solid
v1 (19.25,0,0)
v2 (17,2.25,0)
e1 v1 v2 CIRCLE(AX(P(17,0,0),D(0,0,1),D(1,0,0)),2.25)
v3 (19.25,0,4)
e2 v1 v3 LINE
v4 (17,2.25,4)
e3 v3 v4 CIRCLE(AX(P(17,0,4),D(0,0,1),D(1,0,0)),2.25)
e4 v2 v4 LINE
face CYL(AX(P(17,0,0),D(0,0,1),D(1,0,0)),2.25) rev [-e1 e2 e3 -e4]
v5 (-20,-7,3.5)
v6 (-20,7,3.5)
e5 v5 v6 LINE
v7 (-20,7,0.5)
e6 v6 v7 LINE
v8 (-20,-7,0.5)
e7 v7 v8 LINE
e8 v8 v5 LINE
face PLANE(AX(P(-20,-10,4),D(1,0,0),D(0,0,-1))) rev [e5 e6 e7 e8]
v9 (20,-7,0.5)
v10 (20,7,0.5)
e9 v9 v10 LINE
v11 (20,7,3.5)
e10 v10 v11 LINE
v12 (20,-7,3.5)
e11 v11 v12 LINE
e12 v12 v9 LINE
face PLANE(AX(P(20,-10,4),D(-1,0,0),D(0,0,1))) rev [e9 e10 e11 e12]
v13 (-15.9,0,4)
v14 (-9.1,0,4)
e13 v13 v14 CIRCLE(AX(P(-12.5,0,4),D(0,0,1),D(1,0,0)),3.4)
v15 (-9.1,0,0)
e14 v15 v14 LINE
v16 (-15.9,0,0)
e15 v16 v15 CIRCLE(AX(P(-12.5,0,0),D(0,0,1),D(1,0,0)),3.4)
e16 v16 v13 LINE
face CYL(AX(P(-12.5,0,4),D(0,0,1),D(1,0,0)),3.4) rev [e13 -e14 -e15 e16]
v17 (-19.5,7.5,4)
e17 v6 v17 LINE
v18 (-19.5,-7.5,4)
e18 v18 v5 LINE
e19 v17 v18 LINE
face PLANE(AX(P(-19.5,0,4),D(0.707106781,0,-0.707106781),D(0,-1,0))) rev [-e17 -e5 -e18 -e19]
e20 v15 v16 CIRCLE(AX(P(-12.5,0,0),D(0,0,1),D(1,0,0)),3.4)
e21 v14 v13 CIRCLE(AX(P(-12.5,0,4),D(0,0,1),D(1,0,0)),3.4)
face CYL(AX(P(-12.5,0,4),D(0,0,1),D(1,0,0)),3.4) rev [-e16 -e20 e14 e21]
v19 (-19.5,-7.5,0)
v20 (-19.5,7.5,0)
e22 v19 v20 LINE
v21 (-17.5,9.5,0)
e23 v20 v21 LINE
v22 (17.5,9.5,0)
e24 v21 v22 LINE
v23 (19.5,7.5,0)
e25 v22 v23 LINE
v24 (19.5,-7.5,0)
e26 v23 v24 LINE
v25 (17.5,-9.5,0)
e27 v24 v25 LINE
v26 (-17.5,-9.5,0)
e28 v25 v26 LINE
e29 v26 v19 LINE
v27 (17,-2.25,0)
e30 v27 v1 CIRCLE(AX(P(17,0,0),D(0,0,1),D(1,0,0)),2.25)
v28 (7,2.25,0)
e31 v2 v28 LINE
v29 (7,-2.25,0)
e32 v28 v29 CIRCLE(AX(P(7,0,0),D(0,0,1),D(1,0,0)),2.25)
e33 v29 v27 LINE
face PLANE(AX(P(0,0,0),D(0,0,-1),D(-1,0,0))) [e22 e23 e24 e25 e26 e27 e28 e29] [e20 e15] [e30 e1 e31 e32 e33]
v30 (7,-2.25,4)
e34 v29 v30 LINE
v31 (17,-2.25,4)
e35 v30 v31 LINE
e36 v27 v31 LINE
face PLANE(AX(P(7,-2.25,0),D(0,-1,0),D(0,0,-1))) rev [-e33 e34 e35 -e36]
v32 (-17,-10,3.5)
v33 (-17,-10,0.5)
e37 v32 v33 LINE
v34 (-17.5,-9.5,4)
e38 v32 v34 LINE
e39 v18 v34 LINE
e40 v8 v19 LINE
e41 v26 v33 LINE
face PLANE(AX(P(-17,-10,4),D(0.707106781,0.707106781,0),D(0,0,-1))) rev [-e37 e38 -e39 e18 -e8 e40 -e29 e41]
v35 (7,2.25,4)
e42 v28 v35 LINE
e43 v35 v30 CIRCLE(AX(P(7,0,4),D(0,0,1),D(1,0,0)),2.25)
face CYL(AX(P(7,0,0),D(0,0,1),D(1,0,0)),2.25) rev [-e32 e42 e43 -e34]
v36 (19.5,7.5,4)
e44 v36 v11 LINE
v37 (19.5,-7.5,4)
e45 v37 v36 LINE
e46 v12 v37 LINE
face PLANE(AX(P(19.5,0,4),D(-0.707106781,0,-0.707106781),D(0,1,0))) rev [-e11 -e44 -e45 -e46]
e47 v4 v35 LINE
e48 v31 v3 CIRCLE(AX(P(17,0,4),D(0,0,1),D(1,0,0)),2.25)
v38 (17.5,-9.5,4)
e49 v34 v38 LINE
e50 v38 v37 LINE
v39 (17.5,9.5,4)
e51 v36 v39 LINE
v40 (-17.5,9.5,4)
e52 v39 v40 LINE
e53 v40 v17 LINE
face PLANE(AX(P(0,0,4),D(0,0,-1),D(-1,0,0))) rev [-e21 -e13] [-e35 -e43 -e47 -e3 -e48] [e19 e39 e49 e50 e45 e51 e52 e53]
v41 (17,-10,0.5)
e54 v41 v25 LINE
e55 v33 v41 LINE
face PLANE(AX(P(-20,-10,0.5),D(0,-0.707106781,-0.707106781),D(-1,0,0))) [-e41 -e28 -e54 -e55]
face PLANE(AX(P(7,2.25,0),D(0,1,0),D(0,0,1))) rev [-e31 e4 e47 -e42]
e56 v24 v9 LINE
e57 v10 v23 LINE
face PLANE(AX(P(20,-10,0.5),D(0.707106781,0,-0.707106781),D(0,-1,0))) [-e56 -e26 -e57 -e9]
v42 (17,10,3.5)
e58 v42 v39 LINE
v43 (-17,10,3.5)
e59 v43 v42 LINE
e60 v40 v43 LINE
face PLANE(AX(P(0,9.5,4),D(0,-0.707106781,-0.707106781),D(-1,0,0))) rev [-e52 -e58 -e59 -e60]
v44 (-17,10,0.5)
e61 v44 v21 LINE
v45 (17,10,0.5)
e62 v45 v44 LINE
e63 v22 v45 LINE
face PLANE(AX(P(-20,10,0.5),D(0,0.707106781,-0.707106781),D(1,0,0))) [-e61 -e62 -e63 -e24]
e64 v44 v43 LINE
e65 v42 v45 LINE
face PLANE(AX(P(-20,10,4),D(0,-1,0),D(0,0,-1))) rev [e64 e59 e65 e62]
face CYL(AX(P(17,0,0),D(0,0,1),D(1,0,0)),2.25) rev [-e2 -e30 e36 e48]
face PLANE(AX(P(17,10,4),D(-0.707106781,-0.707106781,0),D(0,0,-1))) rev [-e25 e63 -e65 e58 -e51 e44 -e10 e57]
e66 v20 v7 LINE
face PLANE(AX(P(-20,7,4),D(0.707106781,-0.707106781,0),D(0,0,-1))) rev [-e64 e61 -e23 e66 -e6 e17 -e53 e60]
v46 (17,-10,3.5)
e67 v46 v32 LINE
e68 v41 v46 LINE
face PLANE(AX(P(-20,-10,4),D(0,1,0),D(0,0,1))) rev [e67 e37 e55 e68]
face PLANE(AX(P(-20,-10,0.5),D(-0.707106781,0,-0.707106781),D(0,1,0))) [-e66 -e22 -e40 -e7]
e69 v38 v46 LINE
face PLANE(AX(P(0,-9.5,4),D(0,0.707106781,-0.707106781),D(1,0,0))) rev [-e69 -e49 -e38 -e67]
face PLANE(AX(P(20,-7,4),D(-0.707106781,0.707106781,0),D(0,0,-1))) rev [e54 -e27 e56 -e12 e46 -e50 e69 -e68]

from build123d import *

# Parameters (mm, degrees)
SKETCH1_W           = 40
SKETCH1_H           = 20
BOSS_EXTRUDE1_DEPTH = 4
M8_TAPPED_HOLE1_D   = 6.8
CUT_EXTRUDE1_DEPTH  = 4
CHAMFER1_SIZE       = 3
CHAMFER2_SIZE       = 0.5


with BuildPart() as part:
    # Sketch1 → Boss-Extrude1 (new body)
    with BuildSketch(Plane.XY):
        Rectangle(SKETCH1_W, SKETCH1_H)
    extrude(amount=BOSS_EXTRUDE1_DEPTH)

    # M8 Tapped Hole1 (through all)
    with Locations(Plane.XY.offset(4)):
        with Locations((-12.5, 0)):
            Hole(M8_TAPPED_HOLE1_D / 2)

    # Sketch4 → Cut-Extrude1 (cut)
    with BuildSketch(Plane.XY.offset(4)):
        with BuildLine():
            Line((7, 2.25), (17, 2.25))
            ThreePointArc((17, 2.25), (19.25, 0), (17, -2.25))
            Line((17, -2.25), (7, -2.25))
            ThreePointArc((7, -2.25), (4.75, 0), (7, 2.25))
        make_face()
    extrude(amount=-CUT_EXTRUDE1_DEPTH, mode=Mode.SUBTRACT)

    # Chamfer1
    chamfer1_edges = [part.edges().sort_by_distance(p)[0] for p in [
        (20, -10, 2),
        (-20, -10, 2),
        (-20, 10, 2),
        (20, 10, 2),
    ]]
    chamfer(chamfer1_edges, length=CHAMFER1_SIZE)

    # Chamfer2
    chamfer2_edges = [part.edges().sort_by_distance(p)[0] for p in [
        (20, 0, 0),
        (20, 0, 4),
        (0, -10, 0),
        (-20, 0, 0),
        (0, 10, 0),
        (0, -10, 4),
        (0, 10, 4),
        (-20, 0, 4),
    ]]
    chamfer(chamfer2_edges, length=CHAMFER2_SIZE)


solid = part.part
